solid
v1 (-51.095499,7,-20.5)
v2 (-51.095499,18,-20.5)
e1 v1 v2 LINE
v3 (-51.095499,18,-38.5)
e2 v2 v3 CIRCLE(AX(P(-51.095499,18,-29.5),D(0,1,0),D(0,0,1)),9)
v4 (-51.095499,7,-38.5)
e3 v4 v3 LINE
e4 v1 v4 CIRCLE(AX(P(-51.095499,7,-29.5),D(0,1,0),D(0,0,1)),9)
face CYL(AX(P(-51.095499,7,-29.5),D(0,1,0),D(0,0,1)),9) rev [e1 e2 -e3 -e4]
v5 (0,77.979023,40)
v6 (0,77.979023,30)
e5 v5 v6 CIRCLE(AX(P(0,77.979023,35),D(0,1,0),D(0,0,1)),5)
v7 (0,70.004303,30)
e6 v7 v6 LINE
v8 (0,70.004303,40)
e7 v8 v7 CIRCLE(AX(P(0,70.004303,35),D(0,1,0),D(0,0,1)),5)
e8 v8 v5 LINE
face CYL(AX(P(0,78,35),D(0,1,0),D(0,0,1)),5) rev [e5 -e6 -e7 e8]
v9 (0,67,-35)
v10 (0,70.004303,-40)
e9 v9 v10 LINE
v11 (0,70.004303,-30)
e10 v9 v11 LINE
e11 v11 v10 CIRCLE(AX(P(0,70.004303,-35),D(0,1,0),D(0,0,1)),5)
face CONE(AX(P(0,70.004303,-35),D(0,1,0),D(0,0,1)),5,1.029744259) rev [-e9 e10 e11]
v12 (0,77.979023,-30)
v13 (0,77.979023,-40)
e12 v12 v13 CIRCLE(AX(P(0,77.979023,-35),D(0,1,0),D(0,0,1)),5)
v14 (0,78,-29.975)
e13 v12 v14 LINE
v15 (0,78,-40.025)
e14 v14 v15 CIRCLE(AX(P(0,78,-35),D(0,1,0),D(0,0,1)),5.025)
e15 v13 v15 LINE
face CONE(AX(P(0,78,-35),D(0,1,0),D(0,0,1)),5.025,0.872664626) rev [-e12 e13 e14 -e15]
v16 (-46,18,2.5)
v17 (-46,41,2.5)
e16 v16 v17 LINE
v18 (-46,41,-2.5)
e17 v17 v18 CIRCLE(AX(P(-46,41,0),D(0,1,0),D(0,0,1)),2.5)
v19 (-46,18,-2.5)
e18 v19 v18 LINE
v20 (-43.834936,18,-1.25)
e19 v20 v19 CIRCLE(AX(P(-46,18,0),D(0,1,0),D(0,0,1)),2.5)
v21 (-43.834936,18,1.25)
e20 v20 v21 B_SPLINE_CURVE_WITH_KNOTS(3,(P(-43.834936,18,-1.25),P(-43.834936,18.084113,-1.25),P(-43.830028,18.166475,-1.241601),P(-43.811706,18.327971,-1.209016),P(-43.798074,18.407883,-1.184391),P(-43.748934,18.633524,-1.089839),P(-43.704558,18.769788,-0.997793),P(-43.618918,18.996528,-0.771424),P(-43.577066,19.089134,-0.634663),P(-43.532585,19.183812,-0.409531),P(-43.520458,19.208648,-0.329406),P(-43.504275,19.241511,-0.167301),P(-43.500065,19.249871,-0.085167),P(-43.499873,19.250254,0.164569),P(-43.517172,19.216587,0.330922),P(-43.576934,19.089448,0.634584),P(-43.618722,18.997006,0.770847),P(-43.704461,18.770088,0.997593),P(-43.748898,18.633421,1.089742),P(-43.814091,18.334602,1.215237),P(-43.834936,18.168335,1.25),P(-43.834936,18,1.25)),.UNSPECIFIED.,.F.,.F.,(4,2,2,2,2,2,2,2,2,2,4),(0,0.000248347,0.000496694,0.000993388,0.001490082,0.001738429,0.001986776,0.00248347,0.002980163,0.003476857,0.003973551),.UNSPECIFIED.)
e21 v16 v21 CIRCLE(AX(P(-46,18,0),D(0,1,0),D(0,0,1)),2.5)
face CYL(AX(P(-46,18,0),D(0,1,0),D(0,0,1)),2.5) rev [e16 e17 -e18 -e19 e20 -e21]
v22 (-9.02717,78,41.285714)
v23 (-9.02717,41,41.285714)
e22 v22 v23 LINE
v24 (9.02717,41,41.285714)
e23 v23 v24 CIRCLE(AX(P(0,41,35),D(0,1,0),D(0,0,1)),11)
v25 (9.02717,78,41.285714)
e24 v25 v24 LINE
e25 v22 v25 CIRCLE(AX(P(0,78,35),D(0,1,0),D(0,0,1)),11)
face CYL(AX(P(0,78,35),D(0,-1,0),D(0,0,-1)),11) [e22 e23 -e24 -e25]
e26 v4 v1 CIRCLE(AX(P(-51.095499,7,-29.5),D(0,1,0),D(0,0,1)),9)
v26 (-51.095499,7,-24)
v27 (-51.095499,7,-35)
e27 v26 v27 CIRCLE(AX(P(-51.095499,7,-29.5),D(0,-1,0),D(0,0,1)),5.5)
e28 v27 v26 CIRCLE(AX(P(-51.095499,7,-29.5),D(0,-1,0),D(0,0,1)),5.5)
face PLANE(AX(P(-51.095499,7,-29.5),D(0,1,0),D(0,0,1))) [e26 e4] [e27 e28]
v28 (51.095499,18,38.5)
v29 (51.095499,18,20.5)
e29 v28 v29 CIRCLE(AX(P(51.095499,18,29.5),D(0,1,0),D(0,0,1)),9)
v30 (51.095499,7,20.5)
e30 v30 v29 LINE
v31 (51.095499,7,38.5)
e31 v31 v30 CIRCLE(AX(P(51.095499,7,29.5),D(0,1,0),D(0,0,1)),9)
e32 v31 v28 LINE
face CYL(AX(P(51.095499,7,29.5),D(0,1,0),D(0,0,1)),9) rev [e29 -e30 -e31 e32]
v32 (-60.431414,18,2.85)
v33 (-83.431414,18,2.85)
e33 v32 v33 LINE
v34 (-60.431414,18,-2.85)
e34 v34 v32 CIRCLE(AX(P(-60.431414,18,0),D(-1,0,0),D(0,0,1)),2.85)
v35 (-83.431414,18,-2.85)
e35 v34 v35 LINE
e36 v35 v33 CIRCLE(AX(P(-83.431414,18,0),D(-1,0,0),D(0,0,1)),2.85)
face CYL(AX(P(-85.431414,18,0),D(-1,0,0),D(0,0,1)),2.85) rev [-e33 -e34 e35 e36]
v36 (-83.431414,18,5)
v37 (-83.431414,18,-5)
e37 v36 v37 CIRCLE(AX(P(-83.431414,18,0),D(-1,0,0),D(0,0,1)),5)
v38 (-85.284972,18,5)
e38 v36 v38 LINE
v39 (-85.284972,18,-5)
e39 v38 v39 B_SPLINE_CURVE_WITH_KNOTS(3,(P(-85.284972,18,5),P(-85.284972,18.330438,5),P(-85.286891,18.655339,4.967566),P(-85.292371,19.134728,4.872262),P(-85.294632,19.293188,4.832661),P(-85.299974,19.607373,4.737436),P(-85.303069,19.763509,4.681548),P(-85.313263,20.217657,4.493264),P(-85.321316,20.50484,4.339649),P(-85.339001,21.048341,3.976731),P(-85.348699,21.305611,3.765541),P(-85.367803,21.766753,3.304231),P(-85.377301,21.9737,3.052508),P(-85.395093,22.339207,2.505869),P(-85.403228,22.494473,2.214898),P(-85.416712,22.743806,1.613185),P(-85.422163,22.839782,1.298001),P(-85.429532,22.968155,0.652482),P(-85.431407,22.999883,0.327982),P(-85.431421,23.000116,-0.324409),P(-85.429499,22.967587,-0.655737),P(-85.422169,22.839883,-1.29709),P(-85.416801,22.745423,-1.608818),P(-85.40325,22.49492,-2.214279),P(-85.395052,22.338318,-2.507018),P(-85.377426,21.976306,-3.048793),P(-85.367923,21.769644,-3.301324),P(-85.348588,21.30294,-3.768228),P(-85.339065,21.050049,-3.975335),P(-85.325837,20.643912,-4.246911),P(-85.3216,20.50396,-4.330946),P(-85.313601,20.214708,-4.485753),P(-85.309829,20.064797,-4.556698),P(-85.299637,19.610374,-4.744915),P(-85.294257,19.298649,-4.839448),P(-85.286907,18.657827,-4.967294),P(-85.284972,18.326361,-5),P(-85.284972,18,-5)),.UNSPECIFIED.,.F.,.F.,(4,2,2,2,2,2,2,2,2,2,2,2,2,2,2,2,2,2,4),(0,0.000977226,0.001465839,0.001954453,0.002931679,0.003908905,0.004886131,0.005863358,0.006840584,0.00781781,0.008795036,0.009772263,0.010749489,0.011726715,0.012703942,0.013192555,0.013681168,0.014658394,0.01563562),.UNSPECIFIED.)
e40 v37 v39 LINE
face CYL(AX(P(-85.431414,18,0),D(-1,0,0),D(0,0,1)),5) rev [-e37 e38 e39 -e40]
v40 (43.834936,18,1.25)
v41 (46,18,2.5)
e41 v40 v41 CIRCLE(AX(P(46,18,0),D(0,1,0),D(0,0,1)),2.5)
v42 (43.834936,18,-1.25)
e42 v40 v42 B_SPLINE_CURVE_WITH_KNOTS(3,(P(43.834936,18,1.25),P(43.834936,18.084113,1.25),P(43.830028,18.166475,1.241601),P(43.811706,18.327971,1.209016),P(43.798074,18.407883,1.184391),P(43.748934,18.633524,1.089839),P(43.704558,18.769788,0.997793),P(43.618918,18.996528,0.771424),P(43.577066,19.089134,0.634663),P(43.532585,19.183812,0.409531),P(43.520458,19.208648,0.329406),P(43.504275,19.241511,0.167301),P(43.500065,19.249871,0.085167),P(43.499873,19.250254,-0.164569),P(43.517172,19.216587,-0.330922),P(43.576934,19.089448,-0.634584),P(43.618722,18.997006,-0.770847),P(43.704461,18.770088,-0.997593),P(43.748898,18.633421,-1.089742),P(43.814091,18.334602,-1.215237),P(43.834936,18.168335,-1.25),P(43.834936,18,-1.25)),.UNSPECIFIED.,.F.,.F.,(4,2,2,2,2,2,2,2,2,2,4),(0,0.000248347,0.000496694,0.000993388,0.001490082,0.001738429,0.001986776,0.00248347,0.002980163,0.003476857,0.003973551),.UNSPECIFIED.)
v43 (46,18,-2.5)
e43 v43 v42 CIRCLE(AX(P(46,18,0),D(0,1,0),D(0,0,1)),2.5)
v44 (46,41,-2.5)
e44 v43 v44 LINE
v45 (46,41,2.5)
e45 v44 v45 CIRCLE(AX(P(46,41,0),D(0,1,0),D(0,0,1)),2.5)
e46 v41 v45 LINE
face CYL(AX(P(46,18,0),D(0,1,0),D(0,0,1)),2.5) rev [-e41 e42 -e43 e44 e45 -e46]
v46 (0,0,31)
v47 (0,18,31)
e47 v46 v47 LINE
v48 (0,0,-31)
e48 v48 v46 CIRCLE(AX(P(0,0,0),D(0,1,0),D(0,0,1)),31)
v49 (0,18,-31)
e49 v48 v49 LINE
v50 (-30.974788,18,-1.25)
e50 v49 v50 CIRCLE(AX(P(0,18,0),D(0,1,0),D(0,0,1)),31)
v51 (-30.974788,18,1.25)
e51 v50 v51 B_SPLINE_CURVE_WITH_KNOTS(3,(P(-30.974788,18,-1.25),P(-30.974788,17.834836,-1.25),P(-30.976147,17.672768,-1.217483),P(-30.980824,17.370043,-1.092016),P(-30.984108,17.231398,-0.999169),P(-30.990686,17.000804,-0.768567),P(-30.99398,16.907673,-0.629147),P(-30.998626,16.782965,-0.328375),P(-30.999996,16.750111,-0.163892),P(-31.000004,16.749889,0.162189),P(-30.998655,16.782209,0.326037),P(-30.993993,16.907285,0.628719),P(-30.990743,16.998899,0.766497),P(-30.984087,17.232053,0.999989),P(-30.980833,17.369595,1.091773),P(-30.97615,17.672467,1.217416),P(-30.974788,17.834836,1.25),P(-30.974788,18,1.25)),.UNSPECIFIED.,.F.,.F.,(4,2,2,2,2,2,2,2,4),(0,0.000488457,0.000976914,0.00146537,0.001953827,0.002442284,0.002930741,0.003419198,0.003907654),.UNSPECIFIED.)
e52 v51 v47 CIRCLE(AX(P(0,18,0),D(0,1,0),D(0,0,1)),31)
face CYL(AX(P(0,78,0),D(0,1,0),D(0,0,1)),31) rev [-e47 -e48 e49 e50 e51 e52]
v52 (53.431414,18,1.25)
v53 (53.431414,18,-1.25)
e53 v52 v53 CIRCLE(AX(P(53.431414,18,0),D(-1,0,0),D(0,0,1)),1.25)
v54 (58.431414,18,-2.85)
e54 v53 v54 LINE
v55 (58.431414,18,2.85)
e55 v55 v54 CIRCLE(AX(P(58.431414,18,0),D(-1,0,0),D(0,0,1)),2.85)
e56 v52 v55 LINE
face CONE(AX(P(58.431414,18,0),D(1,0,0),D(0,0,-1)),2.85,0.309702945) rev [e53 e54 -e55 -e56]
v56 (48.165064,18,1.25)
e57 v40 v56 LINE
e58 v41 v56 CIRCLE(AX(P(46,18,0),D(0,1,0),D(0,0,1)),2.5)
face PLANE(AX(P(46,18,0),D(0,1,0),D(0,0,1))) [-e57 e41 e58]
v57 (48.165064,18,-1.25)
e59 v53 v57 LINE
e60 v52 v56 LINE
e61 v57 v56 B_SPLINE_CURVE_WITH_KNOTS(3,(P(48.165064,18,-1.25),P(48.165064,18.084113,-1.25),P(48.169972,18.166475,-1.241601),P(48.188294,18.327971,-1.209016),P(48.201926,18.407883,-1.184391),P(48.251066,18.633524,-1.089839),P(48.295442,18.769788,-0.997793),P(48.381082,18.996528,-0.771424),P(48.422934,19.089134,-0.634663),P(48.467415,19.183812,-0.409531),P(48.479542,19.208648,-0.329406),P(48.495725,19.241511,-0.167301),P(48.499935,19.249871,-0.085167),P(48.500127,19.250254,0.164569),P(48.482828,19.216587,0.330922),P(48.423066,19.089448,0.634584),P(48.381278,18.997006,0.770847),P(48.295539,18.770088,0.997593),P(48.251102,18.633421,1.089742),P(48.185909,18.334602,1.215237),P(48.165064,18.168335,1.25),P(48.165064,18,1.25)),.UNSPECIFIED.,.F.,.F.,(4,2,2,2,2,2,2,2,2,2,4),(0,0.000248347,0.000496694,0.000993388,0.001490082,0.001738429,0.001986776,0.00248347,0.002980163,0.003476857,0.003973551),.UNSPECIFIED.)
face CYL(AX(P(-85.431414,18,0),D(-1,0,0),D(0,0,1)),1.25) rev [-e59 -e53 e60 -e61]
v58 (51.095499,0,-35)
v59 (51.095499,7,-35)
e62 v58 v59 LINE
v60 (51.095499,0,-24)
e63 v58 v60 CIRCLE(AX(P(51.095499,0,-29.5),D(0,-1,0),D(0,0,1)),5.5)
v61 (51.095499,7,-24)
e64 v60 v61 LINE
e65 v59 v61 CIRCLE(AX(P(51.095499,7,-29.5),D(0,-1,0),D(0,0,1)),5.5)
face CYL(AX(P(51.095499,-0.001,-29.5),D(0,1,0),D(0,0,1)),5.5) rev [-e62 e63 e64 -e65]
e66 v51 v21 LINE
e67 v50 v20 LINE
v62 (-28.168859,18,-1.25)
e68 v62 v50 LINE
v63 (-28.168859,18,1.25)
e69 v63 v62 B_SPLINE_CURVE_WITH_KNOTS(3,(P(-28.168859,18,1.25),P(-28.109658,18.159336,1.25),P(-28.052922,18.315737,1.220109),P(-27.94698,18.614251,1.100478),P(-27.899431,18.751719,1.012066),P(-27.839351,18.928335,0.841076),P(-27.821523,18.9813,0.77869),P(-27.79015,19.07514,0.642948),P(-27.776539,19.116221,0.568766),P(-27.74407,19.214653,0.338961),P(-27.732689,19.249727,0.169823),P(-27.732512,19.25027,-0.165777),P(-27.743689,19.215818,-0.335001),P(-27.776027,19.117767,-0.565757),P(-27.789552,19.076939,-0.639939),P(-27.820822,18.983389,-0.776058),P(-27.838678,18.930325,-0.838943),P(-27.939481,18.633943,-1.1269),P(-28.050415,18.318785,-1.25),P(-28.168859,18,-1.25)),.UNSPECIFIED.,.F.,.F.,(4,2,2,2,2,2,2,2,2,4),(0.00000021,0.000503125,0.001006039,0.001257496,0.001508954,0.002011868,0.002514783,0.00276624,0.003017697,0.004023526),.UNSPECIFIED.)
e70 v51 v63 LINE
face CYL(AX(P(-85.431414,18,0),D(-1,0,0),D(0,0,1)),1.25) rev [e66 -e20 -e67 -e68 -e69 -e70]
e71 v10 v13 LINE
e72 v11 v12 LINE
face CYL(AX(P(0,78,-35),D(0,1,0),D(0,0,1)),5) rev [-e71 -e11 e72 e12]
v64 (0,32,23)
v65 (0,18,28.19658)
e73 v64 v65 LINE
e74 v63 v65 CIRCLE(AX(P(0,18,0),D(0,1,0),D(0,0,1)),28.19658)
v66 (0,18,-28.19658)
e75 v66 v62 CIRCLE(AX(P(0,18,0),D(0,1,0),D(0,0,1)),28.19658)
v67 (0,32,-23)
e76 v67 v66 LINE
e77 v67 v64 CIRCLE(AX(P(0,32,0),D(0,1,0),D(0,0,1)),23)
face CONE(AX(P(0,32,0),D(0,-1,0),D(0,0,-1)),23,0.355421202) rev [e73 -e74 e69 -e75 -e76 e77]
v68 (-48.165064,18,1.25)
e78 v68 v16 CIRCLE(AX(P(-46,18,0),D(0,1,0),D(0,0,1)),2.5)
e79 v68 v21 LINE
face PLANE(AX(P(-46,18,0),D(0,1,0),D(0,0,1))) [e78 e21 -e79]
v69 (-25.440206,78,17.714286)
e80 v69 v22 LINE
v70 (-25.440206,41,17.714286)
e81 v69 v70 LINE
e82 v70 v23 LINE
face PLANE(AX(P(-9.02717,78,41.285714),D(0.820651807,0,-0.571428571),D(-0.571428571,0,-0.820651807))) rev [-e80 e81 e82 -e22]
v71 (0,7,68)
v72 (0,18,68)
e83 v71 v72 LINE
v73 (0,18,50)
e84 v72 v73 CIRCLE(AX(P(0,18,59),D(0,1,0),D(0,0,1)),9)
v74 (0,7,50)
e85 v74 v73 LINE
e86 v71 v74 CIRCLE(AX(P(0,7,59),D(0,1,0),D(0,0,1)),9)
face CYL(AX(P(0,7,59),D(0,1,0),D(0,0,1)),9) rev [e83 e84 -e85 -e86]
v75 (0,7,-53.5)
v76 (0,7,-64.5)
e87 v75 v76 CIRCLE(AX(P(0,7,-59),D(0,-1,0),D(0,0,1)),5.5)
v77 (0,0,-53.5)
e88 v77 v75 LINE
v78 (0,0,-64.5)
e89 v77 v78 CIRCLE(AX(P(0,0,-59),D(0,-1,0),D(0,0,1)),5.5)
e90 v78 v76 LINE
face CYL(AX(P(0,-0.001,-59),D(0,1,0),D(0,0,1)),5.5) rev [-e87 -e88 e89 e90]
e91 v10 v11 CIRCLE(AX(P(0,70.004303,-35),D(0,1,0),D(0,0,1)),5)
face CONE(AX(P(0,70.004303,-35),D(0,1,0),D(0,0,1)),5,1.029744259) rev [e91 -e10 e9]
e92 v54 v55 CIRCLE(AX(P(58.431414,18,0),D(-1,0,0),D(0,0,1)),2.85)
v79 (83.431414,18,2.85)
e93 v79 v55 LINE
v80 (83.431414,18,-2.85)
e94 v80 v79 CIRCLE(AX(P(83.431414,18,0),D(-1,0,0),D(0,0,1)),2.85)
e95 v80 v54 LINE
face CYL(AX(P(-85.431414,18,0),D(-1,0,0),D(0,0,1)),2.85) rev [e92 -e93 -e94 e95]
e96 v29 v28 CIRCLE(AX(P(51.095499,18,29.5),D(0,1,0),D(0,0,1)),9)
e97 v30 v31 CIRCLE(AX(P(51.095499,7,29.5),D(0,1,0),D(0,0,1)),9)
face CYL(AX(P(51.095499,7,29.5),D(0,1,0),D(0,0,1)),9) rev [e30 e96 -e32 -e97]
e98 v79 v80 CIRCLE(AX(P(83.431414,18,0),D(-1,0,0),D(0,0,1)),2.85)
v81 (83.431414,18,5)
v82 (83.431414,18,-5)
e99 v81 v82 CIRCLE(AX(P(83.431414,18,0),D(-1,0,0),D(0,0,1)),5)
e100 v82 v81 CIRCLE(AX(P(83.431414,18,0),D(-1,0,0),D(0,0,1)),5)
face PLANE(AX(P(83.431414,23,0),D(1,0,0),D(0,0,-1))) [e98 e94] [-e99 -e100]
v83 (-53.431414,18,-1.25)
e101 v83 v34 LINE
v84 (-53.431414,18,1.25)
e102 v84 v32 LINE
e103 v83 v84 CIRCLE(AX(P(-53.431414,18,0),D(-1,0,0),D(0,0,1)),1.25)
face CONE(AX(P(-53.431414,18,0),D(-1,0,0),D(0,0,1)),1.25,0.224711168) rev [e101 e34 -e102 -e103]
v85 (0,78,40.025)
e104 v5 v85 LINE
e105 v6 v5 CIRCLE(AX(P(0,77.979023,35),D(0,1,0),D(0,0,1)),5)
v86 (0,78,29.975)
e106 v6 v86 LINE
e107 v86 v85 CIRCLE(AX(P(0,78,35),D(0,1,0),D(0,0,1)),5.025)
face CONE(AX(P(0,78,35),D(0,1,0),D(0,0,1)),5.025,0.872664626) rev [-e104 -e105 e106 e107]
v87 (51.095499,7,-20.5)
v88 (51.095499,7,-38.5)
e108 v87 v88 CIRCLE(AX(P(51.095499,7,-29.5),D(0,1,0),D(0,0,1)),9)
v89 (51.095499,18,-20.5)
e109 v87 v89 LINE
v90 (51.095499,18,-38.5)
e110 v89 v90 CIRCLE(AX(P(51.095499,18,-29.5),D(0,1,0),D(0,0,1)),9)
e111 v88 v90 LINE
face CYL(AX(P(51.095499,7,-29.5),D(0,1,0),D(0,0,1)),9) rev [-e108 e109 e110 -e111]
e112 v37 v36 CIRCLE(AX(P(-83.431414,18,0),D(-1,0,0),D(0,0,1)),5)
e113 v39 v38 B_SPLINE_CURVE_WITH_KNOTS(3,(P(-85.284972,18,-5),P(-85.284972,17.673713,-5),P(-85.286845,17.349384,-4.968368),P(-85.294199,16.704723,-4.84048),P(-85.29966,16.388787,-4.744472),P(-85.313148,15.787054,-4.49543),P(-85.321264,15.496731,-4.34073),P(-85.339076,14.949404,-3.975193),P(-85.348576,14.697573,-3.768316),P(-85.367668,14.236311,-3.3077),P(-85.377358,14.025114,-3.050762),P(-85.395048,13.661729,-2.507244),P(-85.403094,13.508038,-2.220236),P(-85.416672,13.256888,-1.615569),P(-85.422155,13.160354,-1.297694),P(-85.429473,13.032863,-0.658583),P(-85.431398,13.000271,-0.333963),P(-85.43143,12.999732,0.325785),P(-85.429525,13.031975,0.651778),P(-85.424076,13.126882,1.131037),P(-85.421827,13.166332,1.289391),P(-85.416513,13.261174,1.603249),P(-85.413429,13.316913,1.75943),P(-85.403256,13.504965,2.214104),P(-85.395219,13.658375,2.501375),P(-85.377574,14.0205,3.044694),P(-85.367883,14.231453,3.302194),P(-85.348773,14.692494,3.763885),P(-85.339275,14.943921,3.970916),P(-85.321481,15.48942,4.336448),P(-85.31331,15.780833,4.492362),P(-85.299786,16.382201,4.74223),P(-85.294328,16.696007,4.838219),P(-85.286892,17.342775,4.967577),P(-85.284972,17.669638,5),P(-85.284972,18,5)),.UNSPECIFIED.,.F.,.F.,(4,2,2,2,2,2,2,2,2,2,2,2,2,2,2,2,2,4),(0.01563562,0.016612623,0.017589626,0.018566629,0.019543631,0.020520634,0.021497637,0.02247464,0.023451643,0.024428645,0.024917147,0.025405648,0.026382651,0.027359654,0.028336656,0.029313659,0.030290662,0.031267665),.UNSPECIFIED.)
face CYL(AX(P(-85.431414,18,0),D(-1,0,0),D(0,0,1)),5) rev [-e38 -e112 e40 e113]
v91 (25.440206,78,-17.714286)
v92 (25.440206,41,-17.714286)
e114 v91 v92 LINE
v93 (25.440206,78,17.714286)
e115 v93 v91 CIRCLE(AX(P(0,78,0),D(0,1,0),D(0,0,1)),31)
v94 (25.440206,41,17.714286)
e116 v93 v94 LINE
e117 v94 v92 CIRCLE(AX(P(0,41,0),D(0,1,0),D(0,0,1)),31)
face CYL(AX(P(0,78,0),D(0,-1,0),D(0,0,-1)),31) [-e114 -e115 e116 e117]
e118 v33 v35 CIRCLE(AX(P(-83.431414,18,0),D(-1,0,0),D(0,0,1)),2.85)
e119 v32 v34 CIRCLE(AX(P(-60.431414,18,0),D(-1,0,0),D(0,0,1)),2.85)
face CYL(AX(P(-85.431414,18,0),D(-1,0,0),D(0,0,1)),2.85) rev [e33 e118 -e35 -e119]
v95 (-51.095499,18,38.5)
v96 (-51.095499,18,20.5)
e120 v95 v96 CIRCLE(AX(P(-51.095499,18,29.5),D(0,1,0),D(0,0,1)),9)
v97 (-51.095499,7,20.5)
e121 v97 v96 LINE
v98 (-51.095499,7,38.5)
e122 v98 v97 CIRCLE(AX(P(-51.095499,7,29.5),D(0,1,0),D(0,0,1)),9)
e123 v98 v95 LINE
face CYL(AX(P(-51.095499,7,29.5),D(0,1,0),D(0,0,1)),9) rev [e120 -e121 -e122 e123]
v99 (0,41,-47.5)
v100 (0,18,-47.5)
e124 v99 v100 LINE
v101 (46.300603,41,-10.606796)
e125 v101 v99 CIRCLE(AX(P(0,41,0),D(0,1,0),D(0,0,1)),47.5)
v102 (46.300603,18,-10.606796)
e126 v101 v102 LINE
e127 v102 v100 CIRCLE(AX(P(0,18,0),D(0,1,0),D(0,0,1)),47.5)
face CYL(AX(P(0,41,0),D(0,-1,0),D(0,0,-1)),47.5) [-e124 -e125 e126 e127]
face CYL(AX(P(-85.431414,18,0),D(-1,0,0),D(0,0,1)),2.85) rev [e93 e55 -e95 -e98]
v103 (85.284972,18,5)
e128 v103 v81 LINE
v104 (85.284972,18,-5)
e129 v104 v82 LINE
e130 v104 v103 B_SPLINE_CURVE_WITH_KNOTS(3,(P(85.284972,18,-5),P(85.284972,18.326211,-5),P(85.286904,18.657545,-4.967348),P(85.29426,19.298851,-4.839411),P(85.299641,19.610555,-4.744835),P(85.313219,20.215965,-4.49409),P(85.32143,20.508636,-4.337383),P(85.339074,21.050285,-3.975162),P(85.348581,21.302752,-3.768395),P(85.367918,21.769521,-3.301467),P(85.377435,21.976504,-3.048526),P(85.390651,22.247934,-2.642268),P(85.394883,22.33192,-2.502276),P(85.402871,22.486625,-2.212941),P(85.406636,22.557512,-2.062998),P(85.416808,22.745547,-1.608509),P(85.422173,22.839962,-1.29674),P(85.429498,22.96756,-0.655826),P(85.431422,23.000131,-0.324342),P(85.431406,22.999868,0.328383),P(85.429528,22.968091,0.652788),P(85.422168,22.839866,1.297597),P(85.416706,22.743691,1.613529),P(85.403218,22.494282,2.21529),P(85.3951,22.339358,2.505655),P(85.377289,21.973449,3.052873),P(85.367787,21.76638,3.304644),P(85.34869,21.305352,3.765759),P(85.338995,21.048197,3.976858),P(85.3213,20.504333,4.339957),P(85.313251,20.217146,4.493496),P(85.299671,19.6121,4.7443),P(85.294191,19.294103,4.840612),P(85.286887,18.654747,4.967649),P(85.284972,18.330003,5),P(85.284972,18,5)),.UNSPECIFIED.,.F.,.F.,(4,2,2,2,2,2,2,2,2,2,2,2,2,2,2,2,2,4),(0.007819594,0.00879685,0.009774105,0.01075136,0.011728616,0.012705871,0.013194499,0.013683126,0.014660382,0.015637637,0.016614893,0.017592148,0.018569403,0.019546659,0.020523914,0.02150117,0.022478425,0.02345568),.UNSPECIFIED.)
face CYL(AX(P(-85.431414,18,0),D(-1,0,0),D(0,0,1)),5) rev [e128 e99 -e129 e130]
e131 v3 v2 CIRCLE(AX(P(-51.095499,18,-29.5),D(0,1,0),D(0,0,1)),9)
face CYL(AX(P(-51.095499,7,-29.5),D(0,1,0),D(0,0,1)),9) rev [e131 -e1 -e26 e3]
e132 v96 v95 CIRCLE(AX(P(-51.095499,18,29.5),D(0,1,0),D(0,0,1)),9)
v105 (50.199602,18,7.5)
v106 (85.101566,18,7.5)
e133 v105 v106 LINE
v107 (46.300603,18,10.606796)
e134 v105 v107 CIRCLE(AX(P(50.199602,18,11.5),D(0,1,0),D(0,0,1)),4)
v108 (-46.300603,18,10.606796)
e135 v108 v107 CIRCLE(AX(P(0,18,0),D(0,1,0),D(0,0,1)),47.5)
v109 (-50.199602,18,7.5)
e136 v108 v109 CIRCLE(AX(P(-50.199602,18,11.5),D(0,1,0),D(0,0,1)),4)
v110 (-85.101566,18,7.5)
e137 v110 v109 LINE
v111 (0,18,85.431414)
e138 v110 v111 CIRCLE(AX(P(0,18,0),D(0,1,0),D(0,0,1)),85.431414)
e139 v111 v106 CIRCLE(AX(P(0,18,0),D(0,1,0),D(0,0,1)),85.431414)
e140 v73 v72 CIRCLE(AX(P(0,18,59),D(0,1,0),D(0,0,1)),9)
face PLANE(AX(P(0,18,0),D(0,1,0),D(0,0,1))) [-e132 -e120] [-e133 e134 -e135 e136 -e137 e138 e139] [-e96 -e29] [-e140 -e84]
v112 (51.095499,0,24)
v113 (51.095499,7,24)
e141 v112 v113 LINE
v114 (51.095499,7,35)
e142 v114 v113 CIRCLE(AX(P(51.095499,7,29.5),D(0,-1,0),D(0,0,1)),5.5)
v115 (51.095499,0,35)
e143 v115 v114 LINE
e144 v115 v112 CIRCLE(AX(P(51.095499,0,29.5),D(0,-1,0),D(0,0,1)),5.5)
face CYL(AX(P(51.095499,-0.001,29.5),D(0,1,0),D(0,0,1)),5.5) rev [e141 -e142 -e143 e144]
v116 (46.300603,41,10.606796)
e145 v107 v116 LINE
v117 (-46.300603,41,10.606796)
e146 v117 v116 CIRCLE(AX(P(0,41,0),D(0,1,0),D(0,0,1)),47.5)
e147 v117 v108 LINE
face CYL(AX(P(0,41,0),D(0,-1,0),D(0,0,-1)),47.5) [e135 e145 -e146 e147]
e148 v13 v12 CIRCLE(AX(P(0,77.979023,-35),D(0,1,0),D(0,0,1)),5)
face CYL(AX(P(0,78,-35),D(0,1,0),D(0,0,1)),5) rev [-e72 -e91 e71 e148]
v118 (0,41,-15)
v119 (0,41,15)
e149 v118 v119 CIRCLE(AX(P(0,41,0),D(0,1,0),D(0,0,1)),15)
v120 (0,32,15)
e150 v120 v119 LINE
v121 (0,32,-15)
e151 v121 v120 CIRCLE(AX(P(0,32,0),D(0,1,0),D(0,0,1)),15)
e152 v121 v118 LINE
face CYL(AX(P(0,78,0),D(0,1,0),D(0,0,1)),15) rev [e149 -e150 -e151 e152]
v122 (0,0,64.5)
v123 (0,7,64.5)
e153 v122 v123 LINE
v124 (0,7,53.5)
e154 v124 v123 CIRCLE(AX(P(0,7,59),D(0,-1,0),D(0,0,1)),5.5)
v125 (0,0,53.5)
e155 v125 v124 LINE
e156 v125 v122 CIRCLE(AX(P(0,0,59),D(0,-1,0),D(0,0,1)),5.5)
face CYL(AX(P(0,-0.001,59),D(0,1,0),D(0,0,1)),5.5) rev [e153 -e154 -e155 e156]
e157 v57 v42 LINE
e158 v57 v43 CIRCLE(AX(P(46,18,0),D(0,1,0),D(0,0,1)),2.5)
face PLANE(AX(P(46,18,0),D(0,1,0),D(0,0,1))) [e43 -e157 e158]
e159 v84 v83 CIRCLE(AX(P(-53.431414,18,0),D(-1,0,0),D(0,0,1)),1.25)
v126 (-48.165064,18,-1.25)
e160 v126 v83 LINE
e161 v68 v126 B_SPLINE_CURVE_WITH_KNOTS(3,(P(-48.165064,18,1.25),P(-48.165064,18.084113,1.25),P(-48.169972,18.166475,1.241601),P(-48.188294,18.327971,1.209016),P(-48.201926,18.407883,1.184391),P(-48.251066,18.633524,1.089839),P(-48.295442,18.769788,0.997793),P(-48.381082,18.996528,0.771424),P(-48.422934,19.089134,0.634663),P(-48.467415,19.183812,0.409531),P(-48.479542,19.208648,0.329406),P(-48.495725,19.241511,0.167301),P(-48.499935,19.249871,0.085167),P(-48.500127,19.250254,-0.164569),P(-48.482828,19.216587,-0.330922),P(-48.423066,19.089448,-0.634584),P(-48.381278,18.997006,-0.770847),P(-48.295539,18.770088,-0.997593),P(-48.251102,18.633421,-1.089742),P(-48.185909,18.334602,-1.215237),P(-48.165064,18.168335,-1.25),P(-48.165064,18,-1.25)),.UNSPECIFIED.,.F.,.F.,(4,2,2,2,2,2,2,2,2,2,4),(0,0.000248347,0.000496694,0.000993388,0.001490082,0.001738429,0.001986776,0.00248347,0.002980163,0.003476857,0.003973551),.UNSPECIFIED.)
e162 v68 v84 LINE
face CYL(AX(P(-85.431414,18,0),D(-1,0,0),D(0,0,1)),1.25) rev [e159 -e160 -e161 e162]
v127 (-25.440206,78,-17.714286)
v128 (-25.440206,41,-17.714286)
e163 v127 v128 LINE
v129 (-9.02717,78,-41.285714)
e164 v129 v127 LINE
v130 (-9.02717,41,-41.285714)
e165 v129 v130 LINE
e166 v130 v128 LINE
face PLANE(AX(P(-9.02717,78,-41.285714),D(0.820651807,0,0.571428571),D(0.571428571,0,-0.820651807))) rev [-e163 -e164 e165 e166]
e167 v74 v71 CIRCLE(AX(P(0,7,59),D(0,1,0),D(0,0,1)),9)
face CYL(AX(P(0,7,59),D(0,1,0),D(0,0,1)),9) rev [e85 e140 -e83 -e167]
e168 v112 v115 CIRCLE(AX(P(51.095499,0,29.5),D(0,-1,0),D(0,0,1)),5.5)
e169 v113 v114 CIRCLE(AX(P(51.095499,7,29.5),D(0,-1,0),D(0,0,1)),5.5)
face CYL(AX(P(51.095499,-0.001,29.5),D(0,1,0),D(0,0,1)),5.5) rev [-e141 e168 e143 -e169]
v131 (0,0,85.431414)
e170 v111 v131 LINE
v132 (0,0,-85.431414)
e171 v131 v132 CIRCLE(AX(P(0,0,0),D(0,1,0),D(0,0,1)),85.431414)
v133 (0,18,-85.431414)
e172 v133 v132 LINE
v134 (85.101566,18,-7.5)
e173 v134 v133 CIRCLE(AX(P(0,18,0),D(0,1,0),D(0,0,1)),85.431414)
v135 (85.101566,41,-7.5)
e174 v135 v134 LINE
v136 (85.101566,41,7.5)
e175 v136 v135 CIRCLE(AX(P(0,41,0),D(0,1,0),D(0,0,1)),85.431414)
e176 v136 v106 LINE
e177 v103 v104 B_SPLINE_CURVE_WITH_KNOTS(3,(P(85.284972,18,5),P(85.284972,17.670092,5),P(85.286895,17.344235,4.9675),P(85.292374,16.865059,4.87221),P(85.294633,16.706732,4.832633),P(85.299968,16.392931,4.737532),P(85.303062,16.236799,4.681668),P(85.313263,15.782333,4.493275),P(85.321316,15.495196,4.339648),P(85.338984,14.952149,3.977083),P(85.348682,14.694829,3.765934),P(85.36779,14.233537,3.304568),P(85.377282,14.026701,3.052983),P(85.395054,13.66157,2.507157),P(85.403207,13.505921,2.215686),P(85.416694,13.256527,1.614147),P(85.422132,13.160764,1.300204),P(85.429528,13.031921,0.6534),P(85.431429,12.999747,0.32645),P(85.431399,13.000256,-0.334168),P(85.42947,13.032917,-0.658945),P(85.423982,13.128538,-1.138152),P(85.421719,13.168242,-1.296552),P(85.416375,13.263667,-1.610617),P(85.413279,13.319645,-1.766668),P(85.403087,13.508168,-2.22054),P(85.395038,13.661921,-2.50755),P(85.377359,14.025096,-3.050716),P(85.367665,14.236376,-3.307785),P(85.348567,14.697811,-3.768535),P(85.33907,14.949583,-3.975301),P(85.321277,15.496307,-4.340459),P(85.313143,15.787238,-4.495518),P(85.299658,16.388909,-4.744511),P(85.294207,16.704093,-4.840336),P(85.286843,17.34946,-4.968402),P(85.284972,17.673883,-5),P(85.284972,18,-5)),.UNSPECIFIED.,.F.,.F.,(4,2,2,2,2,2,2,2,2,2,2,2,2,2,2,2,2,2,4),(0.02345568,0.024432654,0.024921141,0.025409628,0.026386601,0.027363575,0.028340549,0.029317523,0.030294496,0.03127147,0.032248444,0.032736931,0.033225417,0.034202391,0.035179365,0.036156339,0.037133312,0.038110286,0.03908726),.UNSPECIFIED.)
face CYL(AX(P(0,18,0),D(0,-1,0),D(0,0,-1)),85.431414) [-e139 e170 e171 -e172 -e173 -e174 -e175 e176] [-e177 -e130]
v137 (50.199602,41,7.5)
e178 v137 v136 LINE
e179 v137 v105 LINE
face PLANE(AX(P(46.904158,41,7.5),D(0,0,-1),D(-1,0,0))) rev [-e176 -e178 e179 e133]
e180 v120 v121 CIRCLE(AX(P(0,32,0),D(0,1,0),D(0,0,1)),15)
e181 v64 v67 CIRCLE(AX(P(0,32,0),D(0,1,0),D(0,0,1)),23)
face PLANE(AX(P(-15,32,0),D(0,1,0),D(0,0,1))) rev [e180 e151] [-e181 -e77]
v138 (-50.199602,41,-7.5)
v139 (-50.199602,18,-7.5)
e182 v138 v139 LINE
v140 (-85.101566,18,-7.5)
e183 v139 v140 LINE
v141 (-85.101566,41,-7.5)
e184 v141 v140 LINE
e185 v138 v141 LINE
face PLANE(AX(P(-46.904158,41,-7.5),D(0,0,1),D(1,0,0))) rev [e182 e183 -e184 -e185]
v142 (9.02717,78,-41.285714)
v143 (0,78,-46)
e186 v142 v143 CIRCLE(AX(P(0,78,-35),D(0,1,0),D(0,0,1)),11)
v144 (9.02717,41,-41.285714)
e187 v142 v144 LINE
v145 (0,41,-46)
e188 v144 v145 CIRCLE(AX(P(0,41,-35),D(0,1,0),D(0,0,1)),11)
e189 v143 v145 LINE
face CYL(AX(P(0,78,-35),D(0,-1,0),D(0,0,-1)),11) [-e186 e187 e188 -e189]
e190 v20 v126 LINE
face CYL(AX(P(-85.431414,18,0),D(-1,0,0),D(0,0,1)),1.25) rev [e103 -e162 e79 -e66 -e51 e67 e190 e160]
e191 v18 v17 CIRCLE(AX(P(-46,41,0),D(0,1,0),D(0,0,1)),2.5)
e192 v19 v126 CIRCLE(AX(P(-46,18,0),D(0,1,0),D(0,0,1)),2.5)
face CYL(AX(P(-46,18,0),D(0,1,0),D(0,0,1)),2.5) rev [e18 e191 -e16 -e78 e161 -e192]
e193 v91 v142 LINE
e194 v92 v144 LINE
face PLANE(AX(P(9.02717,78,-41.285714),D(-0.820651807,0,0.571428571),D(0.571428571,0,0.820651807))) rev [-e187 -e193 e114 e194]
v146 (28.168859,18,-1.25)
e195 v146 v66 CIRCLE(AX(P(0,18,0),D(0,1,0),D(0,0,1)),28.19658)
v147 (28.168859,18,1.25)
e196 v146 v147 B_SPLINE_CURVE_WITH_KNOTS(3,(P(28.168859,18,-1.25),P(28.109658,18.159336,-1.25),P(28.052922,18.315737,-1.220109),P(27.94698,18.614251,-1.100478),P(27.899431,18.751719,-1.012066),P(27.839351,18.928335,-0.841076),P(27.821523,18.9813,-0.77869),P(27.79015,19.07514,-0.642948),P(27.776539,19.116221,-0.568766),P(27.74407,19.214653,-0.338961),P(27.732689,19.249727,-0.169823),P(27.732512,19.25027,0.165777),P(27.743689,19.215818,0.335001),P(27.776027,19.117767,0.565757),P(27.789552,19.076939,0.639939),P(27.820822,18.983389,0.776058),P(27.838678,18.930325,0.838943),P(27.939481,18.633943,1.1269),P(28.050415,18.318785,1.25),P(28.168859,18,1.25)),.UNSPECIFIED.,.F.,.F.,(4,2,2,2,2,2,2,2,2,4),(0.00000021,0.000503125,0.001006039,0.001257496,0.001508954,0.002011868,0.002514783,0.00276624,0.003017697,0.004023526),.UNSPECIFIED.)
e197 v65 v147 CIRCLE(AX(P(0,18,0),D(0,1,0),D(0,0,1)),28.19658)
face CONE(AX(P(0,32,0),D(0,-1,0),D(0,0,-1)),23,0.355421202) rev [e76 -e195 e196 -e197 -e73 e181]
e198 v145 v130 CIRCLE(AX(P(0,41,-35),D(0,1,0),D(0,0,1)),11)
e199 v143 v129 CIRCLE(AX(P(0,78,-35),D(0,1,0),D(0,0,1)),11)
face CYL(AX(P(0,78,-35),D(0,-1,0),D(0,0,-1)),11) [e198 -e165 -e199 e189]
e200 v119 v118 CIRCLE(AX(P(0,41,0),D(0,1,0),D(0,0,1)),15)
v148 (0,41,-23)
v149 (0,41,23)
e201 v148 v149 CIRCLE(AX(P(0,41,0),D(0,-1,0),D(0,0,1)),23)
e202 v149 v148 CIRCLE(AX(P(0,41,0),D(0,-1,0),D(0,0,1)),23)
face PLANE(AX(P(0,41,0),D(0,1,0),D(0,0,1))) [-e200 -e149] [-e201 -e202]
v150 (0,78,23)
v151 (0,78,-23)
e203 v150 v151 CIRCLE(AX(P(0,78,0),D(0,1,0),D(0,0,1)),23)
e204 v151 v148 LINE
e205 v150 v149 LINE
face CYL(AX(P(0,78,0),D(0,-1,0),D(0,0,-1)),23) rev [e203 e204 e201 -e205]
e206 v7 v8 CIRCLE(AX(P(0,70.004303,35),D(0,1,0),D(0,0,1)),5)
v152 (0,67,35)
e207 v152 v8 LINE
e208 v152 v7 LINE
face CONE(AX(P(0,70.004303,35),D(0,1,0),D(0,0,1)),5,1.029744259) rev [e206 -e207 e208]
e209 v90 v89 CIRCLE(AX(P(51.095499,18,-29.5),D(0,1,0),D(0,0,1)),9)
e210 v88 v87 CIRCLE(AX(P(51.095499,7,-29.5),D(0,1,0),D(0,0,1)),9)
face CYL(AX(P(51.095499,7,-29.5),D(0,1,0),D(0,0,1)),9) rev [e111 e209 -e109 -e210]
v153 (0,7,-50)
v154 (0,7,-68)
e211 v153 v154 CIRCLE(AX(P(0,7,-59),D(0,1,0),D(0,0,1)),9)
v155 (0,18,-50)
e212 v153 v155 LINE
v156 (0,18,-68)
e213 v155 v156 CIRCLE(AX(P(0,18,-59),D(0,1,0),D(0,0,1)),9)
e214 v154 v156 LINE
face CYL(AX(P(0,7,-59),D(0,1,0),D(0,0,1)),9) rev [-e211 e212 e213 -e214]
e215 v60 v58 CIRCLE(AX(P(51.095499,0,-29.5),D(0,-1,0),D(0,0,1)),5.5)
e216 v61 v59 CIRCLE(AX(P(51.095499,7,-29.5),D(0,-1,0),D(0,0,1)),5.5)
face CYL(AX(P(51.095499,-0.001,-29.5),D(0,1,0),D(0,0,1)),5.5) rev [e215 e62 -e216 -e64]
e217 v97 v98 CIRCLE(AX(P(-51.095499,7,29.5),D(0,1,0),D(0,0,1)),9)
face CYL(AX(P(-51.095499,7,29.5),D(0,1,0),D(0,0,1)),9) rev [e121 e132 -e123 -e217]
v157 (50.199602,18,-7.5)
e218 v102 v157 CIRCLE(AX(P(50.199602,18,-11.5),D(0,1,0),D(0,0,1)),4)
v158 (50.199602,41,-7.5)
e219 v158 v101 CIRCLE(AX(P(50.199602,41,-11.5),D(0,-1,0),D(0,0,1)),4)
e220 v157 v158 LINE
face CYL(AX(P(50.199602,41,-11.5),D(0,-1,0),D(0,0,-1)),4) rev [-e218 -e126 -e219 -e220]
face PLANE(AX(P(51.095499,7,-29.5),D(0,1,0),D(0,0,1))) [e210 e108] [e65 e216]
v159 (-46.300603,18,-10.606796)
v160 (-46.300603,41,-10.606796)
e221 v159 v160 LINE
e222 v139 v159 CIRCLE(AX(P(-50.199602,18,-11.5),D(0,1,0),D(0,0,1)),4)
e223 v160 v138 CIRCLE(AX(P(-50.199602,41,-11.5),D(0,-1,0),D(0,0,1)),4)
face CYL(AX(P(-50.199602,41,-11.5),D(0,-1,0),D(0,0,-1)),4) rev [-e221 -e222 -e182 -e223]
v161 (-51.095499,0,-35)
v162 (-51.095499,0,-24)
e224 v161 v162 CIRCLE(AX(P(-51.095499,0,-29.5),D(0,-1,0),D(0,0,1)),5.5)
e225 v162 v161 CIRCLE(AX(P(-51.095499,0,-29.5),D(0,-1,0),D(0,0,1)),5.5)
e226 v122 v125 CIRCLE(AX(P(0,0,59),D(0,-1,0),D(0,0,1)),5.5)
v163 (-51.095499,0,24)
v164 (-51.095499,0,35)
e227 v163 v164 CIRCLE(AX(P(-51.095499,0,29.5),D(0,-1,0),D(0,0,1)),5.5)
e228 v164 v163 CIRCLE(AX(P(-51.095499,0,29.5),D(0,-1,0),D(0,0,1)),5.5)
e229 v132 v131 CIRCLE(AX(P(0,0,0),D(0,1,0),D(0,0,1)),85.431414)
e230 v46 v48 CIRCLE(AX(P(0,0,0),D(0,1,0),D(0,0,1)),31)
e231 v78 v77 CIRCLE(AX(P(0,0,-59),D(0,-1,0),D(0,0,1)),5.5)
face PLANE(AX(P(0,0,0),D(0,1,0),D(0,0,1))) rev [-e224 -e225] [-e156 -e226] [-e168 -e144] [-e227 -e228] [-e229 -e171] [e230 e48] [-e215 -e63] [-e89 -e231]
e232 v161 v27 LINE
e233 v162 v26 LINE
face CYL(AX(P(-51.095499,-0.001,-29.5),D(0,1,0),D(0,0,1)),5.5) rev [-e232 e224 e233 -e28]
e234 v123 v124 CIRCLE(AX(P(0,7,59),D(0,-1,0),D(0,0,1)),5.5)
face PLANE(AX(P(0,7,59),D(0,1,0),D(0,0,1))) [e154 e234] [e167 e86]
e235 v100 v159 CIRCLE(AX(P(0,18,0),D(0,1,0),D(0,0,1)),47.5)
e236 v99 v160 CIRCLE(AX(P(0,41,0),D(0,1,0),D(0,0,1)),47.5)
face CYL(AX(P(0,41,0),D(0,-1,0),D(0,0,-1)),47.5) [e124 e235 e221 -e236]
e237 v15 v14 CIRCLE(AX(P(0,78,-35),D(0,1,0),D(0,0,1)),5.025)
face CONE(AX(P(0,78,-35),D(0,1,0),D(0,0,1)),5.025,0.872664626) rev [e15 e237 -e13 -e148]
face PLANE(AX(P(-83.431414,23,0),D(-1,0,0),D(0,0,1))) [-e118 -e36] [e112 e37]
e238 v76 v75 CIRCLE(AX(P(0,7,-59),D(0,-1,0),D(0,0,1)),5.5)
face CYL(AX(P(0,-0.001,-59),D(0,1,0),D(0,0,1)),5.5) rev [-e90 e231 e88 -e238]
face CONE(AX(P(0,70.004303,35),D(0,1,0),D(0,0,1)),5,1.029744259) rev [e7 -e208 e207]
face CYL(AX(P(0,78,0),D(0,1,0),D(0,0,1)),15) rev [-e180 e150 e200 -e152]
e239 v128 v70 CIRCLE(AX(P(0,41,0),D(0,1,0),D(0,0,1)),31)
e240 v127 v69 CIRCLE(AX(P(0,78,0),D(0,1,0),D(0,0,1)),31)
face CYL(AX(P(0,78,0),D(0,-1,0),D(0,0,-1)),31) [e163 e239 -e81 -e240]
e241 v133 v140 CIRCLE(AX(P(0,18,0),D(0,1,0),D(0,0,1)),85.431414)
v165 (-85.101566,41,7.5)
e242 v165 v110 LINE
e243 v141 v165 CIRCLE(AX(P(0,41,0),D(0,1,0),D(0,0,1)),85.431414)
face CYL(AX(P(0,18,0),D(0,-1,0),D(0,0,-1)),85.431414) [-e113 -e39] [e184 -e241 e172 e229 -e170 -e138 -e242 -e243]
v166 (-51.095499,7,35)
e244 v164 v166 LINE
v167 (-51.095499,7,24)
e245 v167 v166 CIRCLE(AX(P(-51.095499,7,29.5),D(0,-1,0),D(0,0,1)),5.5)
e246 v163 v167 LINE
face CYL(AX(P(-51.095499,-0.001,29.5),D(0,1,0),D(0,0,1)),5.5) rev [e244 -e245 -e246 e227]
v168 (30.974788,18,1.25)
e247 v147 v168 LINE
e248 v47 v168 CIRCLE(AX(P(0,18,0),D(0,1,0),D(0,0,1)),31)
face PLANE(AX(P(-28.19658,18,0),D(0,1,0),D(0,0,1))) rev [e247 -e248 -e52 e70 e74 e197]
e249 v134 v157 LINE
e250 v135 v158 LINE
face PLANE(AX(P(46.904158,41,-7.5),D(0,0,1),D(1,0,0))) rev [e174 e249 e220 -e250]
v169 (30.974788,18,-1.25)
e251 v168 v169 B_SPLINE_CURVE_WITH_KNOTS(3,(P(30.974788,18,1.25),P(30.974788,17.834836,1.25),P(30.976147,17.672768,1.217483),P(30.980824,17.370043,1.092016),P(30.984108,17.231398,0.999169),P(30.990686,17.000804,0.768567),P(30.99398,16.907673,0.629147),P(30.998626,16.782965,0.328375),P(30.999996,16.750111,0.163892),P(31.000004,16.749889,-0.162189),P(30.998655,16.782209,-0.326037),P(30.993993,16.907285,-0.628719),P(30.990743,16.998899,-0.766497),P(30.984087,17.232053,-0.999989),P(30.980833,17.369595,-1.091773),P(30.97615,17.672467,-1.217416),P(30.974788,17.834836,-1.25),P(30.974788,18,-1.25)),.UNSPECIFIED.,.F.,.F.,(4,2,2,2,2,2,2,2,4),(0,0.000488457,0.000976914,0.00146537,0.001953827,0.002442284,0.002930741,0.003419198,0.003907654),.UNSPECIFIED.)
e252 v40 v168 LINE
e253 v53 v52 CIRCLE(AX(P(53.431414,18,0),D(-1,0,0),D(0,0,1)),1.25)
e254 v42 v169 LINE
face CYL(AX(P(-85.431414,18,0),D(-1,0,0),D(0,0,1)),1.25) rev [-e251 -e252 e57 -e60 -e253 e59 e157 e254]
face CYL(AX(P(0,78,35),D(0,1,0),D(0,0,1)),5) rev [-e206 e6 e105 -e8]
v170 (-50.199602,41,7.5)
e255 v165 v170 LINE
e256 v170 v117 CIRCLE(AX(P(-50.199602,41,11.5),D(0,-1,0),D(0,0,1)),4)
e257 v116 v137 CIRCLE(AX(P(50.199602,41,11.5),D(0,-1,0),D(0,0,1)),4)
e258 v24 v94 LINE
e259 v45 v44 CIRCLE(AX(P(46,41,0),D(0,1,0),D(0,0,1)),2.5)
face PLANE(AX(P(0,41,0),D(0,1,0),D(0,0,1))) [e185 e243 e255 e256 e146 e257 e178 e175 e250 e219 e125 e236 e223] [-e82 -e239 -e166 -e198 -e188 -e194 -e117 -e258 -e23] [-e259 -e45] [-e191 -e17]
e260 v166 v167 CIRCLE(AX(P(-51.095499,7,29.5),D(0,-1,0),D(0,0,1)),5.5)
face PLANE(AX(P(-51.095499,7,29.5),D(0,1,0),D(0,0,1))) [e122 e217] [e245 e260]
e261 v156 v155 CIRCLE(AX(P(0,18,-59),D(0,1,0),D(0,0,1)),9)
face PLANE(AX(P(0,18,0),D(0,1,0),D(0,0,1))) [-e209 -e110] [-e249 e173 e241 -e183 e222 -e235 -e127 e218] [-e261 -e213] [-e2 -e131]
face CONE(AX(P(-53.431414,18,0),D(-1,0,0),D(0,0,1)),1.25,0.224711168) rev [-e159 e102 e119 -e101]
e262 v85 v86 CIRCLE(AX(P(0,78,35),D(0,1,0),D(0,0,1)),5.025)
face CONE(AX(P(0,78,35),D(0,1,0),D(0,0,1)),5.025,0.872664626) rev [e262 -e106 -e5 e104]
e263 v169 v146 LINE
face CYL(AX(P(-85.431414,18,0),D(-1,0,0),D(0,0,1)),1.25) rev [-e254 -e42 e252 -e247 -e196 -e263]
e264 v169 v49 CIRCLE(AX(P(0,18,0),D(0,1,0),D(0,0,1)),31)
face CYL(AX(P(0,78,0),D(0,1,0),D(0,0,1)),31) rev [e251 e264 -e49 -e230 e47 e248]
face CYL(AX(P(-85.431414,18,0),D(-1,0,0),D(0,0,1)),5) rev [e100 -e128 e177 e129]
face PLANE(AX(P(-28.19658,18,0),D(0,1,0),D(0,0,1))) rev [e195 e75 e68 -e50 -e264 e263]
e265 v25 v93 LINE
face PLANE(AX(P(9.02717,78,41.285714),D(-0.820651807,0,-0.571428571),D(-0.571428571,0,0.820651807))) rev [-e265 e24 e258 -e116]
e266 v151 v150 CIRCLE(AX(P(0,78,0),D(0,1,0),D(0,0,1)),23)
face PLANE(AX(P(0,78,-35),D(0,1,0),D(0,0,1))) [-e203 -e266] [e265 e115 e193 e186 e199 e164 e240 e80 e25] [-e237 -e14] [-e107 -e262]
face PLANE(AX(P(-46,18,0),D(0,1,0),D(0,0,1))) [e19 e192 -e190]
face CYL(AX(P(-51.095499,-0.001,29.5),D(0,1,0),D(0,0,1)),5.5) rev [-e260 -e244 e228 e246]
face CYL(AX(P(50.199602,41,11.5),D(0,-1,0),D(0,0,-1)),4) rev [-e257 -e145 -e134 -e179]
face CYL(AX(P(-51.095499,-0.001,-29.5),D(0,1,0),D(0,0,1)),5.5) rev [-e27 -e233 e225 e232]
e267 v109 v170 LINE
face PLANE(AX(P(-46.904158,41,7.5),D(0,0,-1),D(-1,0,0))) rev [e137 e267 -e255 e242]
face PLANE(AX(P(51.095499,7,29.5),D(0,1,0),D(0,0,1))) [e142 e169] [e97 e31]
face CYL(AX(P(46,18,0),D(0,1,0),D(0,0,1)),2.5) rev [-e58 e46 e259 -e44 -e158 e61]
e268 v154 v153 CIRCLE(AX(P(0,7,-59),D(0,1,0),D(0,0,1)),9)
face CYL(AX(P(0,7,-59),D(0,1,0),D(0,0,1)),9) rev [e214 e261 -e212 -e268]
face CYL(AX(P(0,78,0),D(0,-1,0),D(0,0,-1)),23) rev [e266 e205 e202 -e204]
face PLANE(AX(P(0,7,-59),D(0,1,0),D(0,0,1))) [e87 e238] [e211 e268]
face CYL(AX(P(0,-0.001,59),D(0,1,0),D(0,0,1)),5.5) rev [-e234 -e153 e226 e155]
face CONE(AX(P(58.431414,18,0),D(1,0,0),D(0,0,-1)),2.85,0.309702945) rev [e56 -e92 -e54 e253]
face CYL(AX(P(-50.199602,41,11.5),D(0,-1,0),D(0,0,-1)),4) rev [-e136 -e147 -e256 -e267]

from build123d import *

# Parameters (mm, degrees)
BASE_FLANGE_SKETCH_R      = 85.431414023
BASE_FLANGE_DEPTH         = 18
HUB_WITH_LUGS_DEPTH       = 23
BOLT_HOLES_6X_11_REACH    = 124.988
BOLT_HOLES_SKETCH_R       = 5.5
COUNTERBORES_SKETCH_R     = 9
COUNTERBORES_6X_18_DEPTH  = 11
HUB_SIDE_CUTS_SKETCH_R    = 2.5
HUB_SIDE_CUTS_DEPTH       = 23
OVAL_PORT_FLANGE_SKETCH_R = 23
OVAL_PORT_FLANGE_DEPTH    = 37
DOWEL_HOLE_10_D           = 10
DOWEL_HOLE_10_DEPTH       = 7.995696905
DOWEL_HOLE_10_CSINK_D     = 10.05
DOWEL_HOLE_10_CSINK_ANGLE = 100
DOWEL_HOLE_10_TIP         = 3.004303095
HUB_FILLET_R4_A_R         = 4
HUB_FILLET_R4_B_R         = 4
HUB_FILLET_R4_C_R         = 4
HUB_FILLET_R4_D_R         = 4


with BuildPart() as part:
    # Base Flange Sketch → Base Flange (new body)
    with BuildSketch(Plane(origin=(0, 0, 0), x_dir=(1, 0, 0), z_dir=(0, 1, 0))):
        with Locations(Location((0, 0, 0), (0, 0, 270))):
            Circle(BASE_FLANGE_SKETCH_R)
    extrude(amount=BASE_FLANGE_DEPTH)

    # Hub with Lugs Sketch → Hub with Lugs (add)
    with BuildSketch(Plane(origin=(0, 18, 0), x_dir=(1, 0, 0), z_dir=(0, 1, 0))):
        with BuildLine():
            Line((-46.904157598, 7.5), (-85.101565802, 7.5))
            ThreePointArc((-85.101565802, 7.5), (-85.431414023, 0), (-85.101565802, -7.5))
            Line((-85.101565802, -7.5), (-46.904157598, -7.5))
            ThreePointArc((-46.904157598, -7.5), (0, -47.5), (46.904157598, -7.5))
            Line((46.904157598, -7.5), (85.101565802, -7.5))
            ThreePointArc((85.101565802, -7.5), (85.431414023, 0), (85.101565802, 7.5))
            Line((85.101565802, 7.5), (46.904157598, 7.5))
            ThreePointArc((46.904157598, 7.5), (0, 47.5), (-46.904157598, 7.5))
        make_face()
    extrude(amount=HUB_WITH_LUGS_DEPTH)

    # Bolt Holes Sketch → Bolt Holes 6xØ11 (cut, up to next)
    with BuildSketch(Plane(origin=(0, 18, 0), x_dir=(1, 0, 0), z_dir=(0, 1, 0)), mode=Mode.PRIVATE) as bolt_holes_6x_11_sk1:
        with Locations(Location((0, 59, 0), (0, 0, 270))):
            Circle(BOLT_HOLES_SKETCH_R)
    bolt_holes_6x_11_tool1 = extrude(bolt_holes_6x_11_sk1.sketch, amount=-BOLT_HOLES_6X_11_REACH, mode=Mode.PRIVATE) & part.part
    # Bolt Holes Sketch → Bolt Holes 6xØ11 (cut, up to next)
    with BuildSketch(Plane(origin=(0, 18, 0), x_dir=(1, 0, 0), z_dir=(0, 1, 0)), mode=Mode.PRIVATE) as bolt_holes_6x_11_sk2:
        with Locations(Location((0, -59, 0), (0, 0, 270))):
            Circle(BOLT_HOLES_SKETCH_R)
    bolt_holes_6x_11_tool2 = extrude(bolt_holes_6x_11_sk2.sketch, amount=-BOLT_HOLES_6X_11_REACH, mode=Mode.PRIVATE) & part.part
    # Bolt Holes Sketch → Bolt Holes 6xØ11 (cut, up to next)
    with BuildSketch(Plane(origin=(0, 18, 0), x_dir=(1, 0, 0), z_dir=(0, 1, 0)), mode=Mode.PRIVATE) as bolt_holes_6x_11_sk3:
        with Locations(Location((51.095498823, 29.5, 0), (0, 0, 270))):
            Circle(BOLT_HOLES_SKETCH_R)
    bolt_holes_6x_11_tool3 = extrude(bolt_holes_6x_11_sk3.sketch, amount=-BOLT_HOLES_6X_11_REACH, mode=Mode.PRIVATE) & part.part
    # Bolt Holes Sketch → Bolt Holes 6xØ11 (cut, up to next)
    with BuildSketch(Plane(origin=(0, 18, 0), x_dir=(1, 0, 0), z_dir=(0, 1, 0)), mode=Mode.PRIVATE) as bolt_holes_6x_11_sk4:
        with Locations(Location((51.095498823, -29.5, 0), (0, 0, 270))):
            Circle(BOLT_HOLES_SKETCH_R)
    bolt_holes_6x_11_tool4 = extrude(bolt_holes_6x_11_sk4.sketch, amount=-BOLT_HOLES_6X_11_REACH, mode=Mode.PRIVATE) & part.part
    # Bolt Holes Sketch → Bolt Holes 6xØ11 (cut, up to next)
    with BuildSketch(Plane(origin=(0, 18, 0), x_dir=(1, 0, 0), z_dir=(0, 1, 0)), mode=Mode.PRIVATE) as bolt_holes_6x_11_sk5:
        with Locations(Location((-51.095498823, -29.5, 0), (0, 0, 270))):
            Circle(BOLT_HOLES_SKETCH_R)
    bolt_holes_6x_11_tool5 = extrude(bolt_holes_6x_11_sk5.sketch, amount=-BOLT_HOLES_6X_11_REACH, mode=Mode.PRIVATE) & part.part
    # Bolt Holes Sketch → Bolt Holes 6xØ11 (cut, up to next)
    with BuildSketch(Plane(origin=(0, 18, 0), x_dir=(1, 0, 0), z_dir=(0, 1, 0)), mode=Mode.PRIVATE) as bolt_holes_6x_11_sk6:
        with Locations(Location((-51.095498823, 29.5, 0), (0, 0, 270))):
            Circle(BOLT_HOLES_SKETCH_R)
    bolt_holes_6x_11_tool6 = extrude(bolt_holes_6x_11_sk6.sketch, amount=-BOLT_HOLES_6X_11_REACH, mode=Mode.PRIVATE) & part.part
    add(bolt_holes_6x_11_tool1.solids().sort_by_distance((0, 18, -59))[0], mode=Mode.SUBTRACT)
    add(bolt_holes_6x_11_tool2.solids().sort_by_distance((0, 18, 59))[0], mode=Mode.SUBTRACT)
    add(bolt_holes_6x_11_tool3.solids().sort_by_distance((51.095499, 18, -29.5))[0], mode=Mode.SUBTRACT)
    add(bolt_holes_6x_11_tool4.solids().sort_by_distance((51.095499, 18, 29.5))[0], mode=Mode.SUBTRACT)
    add(bolt_holes_6x_11_tool5.solids().sort_by_distance((-51.095499, 18, 29.5))[0], mode=Mode.SUBTRACT)
    add(bolt_holes_6x_11_tool6.solids().sort_by_distance((-51.095499, 18, -29.5))[0], mode=Mode.SUBTRACT)

    # Counterbores Sketch → Counterbores 6xØ18 (cut)
    with BuildSketch(Plane(origin=(0, 18, 0), x_dir=(1, 0, 0), z_dir=(0, 1, 0))):
        with Locations(Location((0, 59, 0), (0, 0, 270))):
            Circle(COUNTERBORES_SKETCH_R)
        with Locations(Location((51.095498823, 29.5, 0), (0, 0, 270))):
            Circle(COUNTERBORES_SKETCH_R)
        with Locations(Location((51.095498823, -29.5, 0), (0, 0, 270))):
            Circle(COUNTERBORES_SKETCH_R)
        with Locations(Location((0, -59, 0), (0, 0, 270))):
            Circle(COUNTERBORES_SKETCH_R)
        with Locations(Location((-51.095498823, -29.5, 0), (0, 0, 270))):
            Circle(COUNTERBORES_SKETCH_R)
        with Locations(Location((-51.095498823, 29.5, 0), (0, 0, 270))):
            Circle(COUNTERBORES_SKETCH_R)
    extrude(amount=-COUNTERBORES_6X_18_DEPTH, mode=Mode.SUBTRACT)

    # Central Bore Profile → Central Bore (revolve, cut)
    with BuildSketch(Plane.XY, mode=Mode.PRIVATE) as central_bore_sk:
        Polygon((-85.431414023, 18), (-85.431414023, 23), (-83.431414023, 23), (-83.431414023, 20.85), (-60.431414023, 20.85), (-53.431414023, 19.25), (53.431414023, 19.25), (58.431414023, 20.85), (83.431414023, 20.85), (83.431414023, 23), (85.431414023, 23), (85.431414023, 18), align=None)
    revolve(central_bore_sk.sketch.rotate(Axis((-85.431414023, 18, 0), (1, 0, 0)), 90), axis=Axis((-85.431414023, 18, 0), (1, 0, 0)), mode=Mode.SUBTRACT)

    # Hub Side Cuts Sketch → Hub Side Cuts (cut)
    with BuildSketch(Plane(origin=(0, 41, 0), x_dir=(1, 0, 0), z_dir=(0, 1, 0))):
        with Locations(Location((46, 0, 0), (0, 0, 270))):
            Circle(HUB_SIDE_CUTS_SKETCH_R)
        with Locations(Location((-46, 0, 0), (0, 0, 270))):
            Circle(HUB_SIDE_CUTS_SKETCH_R)
    extrude(amount=-HUB_SIDE_CUTS_DEPTH, mode=Mode.SUBTRACT)

    # Oval Port Flange Sketch → Oval Port Flange (add)
    with BuildSketch(Plane(origin=(0, 41, 0), x_dir=(1, 0, 0), z_dir=(0, 1, 0))):
        with BuildLine():
            Line((-9.027169873, 41.285714286), (-25.440206006, 17.714285714))
            ThreePointArc((-25.440206006, 17.714285714), (-31, 0), (-25.440206006, -17.714285714))
            Line((-25.440206006, -17.714285714), (-9.027169873, -41.285714286))
            ThreePointArc((-9.027169873, -41.285714286), (0, -46), (9.027169873, -41.285714286))
            Line((9.027169873, -41.285714286), (25.440206006, -17.714285714))
            ThreePointArc((25.440206006, -17.714285714), (31, 0), (25.440206006, 17.714285714))
            Line((25.440206006, 17.714285714), (9.027169873, 41.285714286))
            ThreePointArc((9.027169873, 41.285714286), (0, 46), (-9.027169873, 41.285714286))
        make_face()
        with Locations(Location((0, 0, 0), (0, 0, 270))):
            Circle(OVAL_PORT_FLANGE_SKETCH_R, mode=Mode.SUBTRACT)
    extrude(amount=OVAL_PORT_FLANGE_DEPTH)

    # Dowel Hole Ø10
    with Locations(Plane(origin=(0, 78, 0), x_dir=(1, 0, 0), z_dir=(0, 1, 0))):
        with Locations((0, 35), (0, -35)):
            CounterSinkHole(DOWEL_HOLE_10_D / 2, DOWEL_HOLE_10_CSINK_D / 2, depth=DOWEL_HOLE_10_DEPTH, counter_sink_angle=DOWEL_HOLE_10_CSINK_ANGLE)
            with Locations((0, 0, -(DOWEL_HOLE_10_DEPTH + DOWEL_HOLE_10_TIP / 2))):  # 118° drill point
                Cone(0, DOWEL_HOLE_10_D / 2, DOWEL_HOLE_10_TIP, mode=Mode.SUBTRACT)

    # Port Bore Profile → Port Bore (revolve, cut)
    with BuildSketch(Plane.XY, mode=Mode.PRIVATE) as port_bore_sk:
        Polygon((-28.196580072, 18), (-31, 18), (-31, 0), (0, 0), (0, 41), (-15, 41), (-15, 32), (-23, 32), align=None)
    revolve(port_bore_sk.sketch.rotate(Axis((0, 78, 0), (0, -1, 0)), 270), axis=Axis((0, 78, 0), (0, -1, 0)), mode=Mode.SUBTRACT)

    # Hub Fillet R4 A
    hub_fillet_r4_a_edges = [part.edges().sort_by_distance(p)[0] for p in [
        (46.904157598, 29.5, 7.5),
    ]]
    fillet(hub_fillet_r4_a_edges, radius=HUB_FILLET_R4_A_R)

    # Hub Fillet R4 B
    hub_fillet_r4_b_edges = [part.edges().sort_by_distance(p)[0] for p in [
        (46.904157598, 29.5, -7.5),
    ]]
    fillet(hub_fillet_r4_b_edges, radius=HUB_FILLET_R4_B_R)

    # Hub Fillet R4 C
    hub_fillet_r4_c_edges = [part.edges().sort_by_distance(p)[0] for p in [
        (-46.904157598, 29.5, -7.5),
    ]]
    fillet(hub_fillet_r4_c_edges, radius=HUB_FILLET_R4_C_R)

    # Hub Fillet R4 D
    hub_fillet_r4_d_edges = [part.edges().sort_by_distance(p)[0] for p in [
        (-46.904157598, 29.5, 7.5),
    ]]
    fillet(hub_fillet_r4_d_edges, radius=HUB_FILLET_R4_D_R)


solid = part.part
